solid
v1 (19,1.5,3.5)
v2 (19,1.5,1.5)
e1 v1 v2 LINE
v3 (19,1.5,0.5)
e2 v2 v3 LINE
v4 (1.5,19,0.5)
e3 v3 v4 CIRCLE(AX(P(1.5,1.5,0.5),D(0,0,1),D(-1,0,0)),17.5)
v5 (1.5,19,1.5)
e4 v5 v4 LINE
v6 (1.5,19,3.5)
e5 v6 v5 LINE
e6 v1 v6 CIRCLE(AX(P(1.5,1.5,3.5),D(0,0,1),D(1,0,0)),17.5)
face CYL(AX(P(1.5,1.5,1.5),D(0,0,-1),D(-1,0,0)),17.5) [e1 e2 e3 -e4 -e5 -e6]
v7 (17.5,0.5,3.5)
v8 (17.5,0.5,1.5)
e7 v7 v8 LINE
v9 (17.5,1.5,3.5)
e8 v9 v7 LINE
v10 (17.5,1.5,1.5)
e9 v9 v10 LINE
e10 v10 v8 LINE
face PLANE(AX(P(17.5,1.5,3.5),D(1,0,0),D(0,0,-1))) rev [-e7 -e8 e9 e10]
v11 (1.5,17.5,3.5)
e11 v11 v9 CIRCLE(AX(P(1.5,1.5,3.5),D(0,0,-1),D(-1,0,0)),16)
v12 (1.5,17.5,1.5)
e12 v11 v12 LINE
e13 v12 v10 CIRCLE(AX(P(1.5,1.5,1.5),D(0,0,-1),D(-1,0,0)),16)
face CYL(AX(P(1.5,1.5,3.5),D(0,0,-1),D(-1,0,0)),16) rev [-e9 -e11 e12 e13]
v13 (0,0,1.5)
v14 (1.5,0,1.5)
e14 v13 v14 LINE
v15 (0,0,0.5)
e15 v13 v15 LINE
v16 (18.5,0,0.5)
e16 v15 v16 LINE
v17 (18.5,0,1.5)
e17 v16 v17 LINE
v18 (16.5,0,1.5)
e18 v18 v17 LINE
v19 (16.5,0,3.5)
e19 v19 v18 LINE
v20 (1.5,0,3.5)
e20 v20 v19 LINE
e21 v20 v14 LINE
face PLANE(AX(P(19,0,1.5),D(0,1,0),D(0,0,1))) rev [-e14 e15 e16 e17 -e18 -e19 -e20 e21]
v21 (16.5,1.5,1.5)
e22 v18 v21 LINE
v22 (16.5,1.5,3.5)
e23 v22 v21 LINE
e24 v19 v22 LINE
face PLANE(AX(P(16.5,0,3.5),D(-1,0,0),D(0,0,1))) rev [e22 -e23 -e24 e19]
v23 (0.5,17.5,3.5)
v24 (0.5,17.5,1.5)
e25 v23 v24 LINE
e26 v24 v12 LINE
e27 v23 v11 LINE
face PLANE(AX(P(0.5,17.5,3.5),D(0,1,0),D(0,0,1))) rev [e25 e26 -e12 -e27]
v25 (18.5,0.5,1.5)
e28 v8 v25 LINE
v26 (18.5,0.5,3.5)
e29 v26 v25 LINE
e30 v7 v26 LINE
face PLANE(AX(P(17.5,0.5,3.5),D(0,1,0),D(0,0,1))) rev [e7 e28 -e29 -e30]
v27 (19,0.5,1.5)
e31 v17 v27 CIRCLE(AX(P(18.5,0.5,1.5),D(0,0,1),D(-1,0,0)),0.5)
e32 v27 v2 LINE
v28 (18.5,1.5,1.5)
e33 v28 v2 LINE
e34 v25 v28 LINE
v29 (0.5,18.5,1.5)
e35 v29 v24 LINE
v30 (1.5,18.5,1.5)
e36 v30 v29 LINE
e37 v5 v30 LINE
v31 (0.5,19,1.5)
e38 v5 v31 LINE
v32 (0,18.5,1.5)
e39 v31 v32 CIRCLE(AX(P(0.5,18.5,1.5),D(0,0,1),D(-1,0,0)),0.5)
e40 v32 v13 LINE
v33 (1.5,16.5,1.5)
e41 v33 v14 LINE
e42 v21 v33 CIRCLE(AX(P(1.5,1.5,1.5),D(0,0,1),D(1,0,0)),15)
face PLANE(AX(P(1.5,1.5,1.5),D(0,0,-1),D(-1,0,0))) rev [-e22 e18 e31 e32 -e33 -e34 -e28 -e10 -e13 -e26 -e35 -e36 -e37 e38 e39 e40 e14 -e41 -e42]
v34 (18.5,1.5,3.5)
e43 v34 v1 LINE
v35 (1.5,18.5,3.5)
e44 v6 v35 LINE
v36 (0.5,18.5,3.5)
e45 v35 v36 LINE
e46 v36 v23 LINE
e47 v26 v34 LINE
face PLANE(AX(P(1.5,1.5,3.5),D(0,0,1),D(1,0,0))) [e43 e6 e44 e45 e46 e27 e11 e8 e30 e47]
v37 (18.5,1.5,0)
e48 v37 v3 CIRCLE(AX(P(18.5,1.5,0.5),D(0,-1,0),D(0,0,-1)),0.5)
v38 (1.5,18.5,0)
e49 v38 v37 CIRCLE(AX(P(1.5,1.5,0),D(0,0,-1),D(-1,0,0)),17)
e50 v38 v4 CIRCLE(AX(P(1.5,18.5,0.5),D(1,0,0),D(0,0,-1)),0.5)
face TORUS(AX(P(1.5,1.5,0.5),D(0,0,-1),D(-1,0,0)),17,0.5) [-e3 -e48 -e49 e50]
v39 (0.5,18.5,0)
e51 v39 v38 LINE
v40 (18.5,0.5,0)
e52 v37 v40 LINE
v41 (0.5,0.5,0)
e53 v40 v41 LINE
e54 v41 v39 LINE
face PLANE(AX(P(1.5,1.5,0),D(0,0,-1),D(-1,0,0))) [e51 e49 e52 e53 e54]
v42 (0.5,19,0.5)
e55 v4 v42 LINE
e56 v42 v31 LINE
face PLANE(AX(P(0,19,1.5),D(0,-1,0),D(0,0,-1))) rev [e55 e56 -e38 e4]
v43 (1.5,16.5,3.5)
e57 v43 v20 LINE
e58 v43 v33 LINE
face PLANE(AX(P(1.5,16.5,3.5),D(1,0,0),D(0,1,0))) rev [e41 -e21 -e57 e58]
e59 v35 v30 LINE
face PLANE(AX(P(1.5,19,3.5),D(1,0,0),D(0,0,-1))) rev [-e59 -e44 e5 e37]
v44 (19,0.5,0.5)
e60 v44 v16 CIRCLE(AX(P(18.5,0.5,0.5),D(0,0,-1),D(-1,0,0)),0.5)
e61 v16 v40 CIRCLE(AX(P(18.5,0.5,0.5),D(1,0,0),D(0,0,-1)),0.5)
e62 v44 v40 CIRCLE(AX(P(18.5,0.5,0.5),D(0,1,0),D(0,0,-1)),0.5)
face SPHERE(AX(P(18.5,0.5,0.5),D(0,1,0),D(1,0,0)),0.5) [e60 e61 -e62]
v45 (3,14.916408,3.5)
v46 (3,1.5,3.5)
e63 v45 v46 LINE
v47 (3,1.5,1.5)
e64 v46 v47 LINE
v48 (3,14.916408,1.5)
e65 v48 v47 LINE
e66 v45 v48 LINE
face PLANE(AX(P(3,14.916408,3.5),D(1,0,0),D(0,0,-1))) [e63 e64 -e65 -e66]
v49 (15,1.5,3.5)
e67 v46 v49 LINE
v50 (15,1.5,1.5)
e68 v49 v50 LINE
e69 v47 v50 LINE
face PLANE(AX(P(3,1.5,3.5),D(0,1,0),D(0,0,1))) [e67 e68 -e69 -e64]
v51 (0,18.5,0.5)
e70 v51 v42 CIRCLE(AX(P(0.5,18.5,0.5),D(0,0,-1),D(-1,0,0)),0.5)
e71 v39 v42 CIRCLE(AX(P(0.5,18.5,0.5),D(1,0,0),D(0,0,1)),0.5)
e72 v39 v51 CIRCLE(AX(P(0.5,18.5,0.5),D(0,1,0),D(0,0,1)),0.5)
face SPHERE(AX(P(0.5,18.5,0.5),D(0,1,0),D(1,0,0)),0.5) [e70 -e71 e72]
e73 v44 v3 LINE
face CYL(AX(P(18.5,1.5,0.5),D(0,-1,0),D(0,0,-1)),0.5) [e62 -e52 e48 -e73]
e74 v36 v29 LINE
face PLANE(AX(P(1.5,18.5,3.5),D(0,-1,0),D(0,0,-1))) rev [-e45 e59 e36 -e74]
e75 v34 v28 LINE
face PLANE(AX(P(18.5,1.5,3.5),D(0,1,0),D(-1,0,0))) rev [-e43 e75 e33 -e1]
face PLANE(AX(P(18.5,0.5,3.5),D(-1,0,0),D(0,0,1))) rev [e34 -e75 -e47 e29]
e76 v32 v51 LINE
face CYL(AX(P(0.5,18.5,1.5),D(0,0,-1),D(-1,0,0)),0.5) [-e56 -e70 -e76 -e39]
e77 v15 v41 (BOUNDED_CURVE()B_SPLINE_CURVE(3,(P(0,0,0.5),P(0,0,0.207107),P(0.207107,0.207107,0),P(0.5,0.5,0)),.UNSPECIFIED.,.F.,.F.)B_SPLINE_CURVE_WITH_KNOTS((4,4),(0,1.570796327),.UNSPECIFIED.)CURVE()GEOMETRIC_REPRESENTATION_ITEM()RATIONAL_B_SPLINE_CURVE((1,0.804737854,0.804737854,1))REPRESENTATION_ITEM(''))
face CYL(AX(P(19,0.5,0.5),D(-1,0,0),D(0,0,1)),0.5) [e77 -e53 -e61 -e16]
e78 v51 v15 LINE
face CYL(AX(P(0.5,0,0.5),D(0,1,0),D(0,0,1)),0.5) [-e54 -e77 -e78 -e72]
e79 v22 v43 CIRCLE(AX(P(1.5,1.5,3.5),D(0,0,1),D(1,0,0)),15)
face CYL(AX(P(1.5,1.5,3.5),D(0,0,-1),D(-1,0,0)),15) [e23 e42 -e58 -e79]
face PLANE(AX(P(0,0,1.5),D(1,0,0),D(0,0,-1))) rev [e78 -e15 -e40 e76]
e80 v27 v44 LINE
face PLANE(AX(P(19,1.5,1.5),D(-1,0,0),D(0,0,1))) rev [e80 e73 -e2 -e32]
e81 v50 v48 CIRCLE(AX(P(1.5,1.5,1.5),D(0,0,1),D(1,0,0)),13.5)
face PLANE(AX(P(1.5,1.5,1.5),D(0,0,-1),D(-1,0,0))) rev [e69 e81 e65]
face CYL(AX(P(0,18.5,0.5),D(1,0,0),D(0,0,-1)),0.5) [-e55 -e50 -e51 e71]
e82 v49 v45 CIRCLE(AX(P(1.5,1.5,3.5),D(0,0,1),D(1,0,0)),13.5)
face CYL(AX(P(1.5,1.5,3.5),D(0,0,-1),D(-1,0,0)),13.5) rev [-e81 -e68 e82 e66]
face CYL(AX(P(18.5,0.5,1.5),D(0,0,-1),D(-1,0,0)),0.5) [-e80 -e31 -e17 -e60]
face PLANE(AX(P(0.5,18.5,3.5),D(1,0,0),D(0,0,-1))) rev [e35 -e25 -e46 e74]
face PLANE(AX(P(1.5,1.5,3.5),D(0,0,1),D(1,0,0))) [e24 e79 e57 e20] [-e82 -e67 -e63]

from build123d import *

# Parameters (mm, degrees)
BOSS_EXTRUDE1_DEPTH = 1.5
BOSS_EXTRUDE2_DEPTH = 2
FILETE1_R           = 0.5


with BuildPart() as part:
    # Sketch1 → Boss-Extrude1 (new body)
    with BuildSketch(Plane.XY):
        with BuildLine():
            Line((0, 0), (0, 19))
            Line((0, 19), (1.5, 19))
            ThreePointArc((1.5, 19), (13.874368671, 13.874368671), (19, 1.5))
            Line((19, 1.5), (19, 0))
            Line((19, 0), (0, 0))
        make_face()
    extrude(amount=BOSS_EXTRUDE1_DEPTH)

    # Sketch2 → Boss-Extrude2 (add)
    # profile 1 of 2: a face of its own
    with BuildSketch(Plane.XY.offset(1.5)):
        with BuildLine():
            Line((1.5, 19), (1.5, 18.5))
            Line((1.5, 18.5), (0.5, 18.5))
            Line((0.5, 18.5), (0.5, 17.5))
            Line((0.5, 17.5), (1.5, 17.5))
            ThreePointArc((1.5, 17.5), (12.813708499, 12.813708499), (17.5, 1.5))
            Line((17.5, 1.5), (17.5, 0.5))
            Line((17.5, 0.5), (18.5, 0.5))
            Line((18.5, 0.5), (18.5, 1.5))
            Line((18.5, 1.5), (19, 1.5))
            ThreePointArc((19, 1.5), (13.874368671, 13.874368671), (1.5, 19))
        make_face()
    # profile 2 of 2: a face of its own
    with BuildSketch(Plane.XY.offset(1.5)):
        with BuildLine():
            Line((1.5, 16.5), (1.5, 0))
            Line((1.5, 0), (16.5, 0))
            Line((16.5, 0), (16.5, 1.5))
            ThreePointArc((16.5, 1.5), (12.106601718, 12.106601718), (1.5, 16.5))
        make_face()
        with BuildLine():
            Line((3, 14.916407865), (3, 1.5))
            Line((3, 1.5), (15, 1.5))
            ThreePointArc((15, 1.5), (11.562305899, 10.5), (3, 14.916407865))
        make_face(mode=Mode.SUBTRACT)
    extrude(amount=BOSS_EXTRUDE2_DEPTH)

    # Filete1
    filete1_edges = [part.edges().sort_by_distance(p)[0] for p in [
        (0, 9.5, 0),
        (0.75, 19, 0),
        (13.874368671, 13.874368671, 0),
        (19, 0.75, 0),
        (9.5, 0, 0),
        (0, 19, 0.75),
        (19, 0, 0.75),
    ]]
    fillet(filete1_edges, radius=FILETE1_R)


solid = part.part
